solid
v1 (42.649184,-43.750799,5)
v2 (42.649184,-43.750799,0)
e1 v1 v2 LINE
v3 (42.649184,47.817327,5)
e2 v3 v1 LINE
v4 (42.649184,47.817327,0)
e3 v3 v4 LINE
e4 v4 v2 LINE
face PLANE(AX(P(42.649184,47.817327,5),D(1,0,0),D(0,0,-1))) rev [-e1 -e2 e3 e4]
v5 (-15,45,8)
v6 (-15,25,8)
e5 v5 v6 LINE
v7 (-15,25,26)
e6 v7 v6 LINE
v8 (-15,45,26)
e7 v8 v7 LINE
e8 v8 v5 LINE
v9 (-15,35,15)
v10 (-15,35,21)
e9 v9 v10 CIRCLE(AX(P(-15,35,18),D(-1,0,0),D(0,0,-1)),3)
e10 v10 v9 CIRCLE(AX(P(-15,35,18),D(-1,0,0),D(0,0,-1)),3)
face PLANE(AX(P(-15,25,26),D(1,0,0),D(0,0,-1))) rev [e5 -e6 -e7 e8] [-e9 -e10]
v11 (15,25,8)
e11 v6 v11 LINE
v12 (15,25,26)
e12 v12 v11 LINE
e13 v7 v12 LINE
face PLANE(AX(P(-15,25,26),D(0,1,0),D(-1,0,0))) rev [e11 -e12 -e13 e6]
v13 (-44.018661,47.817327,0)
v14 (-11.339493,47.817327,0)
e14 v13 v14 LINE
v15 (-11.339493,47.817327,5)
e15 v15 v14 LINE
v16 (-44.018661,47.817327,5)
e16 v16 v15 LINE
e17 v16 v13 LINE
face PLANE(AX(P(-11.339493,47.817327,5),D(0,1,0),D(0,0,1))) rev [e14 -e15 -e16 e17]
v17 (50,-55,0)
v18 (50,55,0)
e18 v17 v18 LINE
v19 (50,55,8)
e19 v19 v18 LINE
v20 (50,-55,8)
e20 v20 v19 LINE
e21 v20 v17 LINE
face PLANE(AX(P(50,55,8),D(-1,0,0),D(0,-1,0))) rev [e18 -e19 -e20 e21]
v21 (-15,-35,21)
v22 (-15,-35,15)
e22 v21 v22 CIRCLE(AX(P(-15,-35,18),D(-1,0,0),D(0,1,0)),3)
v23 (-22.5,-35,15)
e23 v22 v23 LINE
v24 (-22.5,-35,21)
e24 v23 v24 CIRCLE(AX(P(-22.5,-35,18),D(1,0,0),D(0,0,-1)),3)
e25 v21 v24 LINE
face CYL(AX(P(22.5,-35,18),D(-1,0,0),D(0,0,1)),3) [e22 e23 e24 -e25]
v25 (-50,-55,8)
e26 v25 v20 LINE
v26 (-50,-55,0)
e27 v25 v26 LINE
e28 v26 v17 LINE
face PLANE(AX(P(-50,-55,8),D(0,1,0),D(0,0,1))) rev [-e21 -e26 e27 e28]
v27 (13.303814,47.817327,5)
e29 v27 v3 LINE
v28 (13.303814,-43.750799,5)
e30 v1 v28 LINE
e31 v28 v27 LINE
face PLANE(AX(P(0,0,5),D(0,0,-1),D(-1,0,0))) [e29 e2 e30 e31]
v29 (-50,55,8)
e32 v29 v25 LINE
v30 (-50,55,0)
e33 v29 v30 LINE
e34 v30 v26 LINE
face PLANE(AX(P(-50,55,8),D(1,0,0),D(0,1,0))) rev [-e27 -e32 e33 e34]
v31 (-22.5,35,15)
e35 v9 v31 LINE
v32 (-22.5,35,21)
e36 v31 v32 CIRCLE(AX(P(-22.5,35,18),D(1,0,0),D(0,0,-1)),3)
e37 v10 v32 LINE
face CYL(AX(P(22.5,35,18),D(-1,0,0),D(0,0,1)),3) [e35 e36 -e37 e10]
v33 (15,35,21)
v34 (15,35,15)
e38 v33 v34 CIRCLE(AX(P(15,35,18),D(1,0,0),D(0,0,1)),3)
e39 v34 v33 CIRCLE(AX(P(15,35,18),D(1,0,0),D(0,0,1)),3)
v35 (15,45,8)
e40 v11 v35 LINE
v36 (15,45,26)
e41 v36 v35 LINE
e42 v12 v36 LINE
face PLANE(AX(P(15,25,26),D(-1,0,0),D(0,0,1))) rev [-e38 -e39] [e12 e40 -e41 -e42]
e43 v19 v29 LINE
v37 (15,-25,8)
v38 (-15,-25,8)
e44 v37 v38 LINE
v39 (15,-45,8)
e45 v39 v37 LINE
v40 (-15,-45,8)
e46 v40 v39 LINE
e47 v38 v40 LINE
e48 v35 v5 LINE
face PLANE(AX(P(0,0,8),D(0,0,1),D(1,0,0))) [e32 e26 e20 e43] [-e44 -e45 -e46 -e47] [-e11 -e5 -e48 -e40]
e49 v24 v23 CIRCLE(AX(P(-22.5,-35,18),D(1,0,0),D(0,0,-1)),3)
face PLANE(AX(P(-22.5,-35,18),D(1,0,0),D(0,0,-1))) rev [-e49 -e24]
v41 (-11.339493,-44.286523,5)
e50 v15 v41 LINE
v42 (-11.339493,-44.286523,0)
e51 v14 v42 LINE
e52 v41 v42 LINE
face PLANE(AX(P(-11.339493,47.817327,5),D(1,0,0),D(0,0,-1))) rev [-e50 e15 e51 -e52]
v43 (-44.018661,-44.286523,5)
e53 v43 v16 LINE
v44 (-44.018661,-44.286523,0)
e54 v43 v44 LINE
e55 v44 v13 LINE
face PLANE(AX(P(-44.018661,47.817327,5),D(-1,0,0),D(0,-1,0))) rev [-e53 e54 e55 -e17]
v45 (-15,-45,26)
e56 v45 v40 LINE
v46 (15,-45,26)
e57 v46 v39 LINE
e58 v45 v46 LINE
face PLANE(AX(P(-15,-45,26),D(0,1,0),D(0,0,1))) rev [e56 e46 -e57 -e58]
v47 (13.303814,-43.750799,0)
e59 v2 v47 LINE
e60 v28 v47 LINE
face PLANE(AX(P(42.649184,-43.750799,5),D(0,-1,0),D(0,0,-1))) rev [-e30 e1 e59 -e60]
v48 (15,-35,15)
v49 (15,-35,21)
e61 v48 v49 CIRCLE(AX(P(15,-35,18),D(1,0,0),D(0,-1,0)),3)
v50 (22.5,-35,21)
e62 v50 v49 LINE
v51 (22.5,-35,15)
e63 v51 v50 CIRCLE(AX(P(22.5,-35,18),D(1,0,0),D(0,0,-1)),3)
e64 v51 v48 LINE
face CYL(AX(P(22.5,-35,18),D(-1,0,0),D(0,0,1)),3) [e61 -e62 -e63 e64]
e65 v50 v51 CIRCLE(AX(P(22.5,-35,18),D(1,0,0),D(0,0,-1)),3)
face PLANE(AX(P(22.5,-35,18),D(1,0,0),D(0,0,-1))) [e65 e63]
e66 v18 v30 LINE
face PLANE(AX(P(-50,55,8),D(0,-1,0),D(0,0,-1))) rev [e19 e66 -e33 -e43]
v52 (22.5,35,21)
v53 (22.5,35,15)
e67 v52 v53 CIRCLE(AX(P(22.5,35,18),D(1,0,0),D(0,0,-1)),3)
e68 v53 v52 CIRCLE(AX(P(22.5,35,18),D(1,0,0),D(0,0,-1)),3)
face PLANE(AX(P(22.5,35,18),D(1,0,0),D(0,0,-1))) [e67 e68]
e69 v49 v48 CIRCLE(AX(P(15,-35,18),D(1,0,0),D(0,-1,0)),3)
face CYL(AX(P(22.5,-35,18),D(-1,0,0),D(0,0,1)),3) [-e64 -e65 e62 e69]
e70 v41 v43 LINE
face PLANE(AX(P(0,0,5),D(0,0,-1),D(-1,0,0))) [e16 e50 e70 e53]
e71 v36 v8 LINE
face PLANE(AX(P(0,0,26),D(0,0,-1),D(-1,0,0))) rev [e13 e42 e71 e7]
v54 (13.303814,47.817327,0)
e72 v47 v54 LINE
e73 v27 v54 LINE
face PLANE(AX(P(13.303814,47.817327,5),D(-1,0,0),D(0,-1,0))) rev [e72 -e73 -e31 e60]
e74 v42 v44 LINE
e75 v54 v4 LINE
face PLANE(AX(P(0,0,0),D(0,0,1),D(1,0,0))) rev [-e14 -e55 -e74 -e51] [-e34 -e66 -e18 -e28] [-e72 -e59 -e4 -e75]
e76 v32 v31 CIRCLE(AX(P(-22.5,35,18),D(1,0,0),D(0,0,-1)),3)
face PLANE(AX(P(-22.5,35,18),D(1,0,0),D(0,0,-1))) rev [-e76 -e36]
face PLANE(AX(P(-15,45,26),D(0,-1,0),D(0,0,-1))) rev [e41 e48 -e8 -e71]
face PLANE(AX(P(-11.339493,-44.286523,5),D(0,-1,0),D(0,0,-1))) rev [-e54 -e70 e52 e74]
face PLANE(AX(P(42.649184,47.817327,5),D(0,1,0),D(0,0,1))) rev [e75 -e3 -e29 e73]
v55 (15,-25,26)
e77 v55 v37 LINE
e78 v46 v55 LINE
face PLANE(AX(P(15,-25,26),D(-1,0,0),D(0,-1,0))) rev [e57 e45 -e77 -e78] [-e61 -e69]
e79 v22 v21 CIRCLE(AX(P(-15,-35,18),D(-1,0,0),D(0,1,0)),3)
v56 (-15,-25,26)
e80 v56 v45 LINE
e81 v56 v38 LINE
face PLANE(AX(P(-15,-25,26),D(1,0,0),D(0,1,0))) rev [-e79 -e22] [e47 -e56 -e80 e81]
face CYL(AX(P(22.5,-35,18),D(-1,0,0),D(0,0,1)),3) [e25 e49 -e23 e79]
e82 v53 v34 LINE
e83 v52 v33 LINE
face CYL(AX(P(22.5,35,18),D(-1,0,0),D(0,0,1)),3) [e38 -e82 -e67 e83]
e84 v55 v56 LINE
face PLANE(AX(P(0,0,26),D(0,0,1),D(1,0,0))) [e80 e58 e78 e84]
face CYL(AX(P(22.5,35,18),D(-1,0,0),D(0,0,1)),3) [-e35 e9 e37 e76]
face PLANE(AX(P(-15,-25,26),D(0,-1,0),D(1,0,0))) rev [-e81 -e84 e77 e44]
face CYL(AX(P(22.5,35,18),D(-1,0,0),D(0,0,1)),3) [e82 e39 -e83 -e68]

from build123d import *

# Parameters (mm, degrees)
SKETCH1_W           = 100
SKETCH1_H           = 110
BOSS_EXTRUDE1_DEPTH = 8
SKETCH2_W           = 30
SKETCH2_H           = 20
BOSS_EXTRUDE2_DEPTH = 18
SKETCH4_W           = 29.345369705
SKETCH4_H           = 91.568125834
SKETCH4_W_2         = 32.679168461
SKETCH4_H_2         = 92.103849907
CUT_EXTRUDE2_DEPTH  = 5
SKETCH3_R           = 3
BOSS_EXTRUDE3_DEPTH = 22.5


with BuildPart() as part:
    # Sketch1 → Boss-Extrude1 (new body)
    with BuildSketch(Plane.XY):
        Rectangle(SKETCH1_W, SKETCH1_H)
    extrude(amount=BOSS_EXTRUDE1_DEPTH)

    # Sketch2 → Boss-Extrude2 (add)
    with BuildSketch(Plane.XY.offset(8)):
        with Locations((0, 35)):
            Rectangle(SKETCH2_W, SKETCH2_H)
        with Locations((0, -35)):
            Rectangle(SKETCH2_W, SKETCH2_H)
    extrude(amount=BOSS_EXTRUDE2_DEPTH)

    # Sketch4 → Cut-Extrude2 (cut)
    with BuildSketch(Plane(origin=(0, 0, 0), x_dir=(-1, 0, 0), z_dir=(0, 0, -1))):
        with Locations((-27.976499336, 2.033263611)):
            Rectangle(SKETCH4_W, SKETCH4_H)
        with Locations((27.679077111, 1.765401575)):
            Rectangle(SKETCH4_W_2, SKETCH4_H_2)
    extrude(amount=-CUT_EXTRUDE2_DEPTH, mode=Mode.SUBTRACT)

    # Sketch3 → Boss-Extrude3 (add, symmetric)
    with BuildSketch(Plane(origin=(0, 0, 0), x_dir=(0, 0, -1), z_dir=(1, 0, 0))):
        with Locations(Location((-18, 35, 0), (0, 0, 180))):
            Circle(SKETCH3_R)
        with Locations(Location((-18, -35, 0), (0, 0, 180))):
            Circle(SKETCH3_R)
    extrude(amount=BOSS_EXTRUDE3_DEPTH, both=True)


solid = part.part
